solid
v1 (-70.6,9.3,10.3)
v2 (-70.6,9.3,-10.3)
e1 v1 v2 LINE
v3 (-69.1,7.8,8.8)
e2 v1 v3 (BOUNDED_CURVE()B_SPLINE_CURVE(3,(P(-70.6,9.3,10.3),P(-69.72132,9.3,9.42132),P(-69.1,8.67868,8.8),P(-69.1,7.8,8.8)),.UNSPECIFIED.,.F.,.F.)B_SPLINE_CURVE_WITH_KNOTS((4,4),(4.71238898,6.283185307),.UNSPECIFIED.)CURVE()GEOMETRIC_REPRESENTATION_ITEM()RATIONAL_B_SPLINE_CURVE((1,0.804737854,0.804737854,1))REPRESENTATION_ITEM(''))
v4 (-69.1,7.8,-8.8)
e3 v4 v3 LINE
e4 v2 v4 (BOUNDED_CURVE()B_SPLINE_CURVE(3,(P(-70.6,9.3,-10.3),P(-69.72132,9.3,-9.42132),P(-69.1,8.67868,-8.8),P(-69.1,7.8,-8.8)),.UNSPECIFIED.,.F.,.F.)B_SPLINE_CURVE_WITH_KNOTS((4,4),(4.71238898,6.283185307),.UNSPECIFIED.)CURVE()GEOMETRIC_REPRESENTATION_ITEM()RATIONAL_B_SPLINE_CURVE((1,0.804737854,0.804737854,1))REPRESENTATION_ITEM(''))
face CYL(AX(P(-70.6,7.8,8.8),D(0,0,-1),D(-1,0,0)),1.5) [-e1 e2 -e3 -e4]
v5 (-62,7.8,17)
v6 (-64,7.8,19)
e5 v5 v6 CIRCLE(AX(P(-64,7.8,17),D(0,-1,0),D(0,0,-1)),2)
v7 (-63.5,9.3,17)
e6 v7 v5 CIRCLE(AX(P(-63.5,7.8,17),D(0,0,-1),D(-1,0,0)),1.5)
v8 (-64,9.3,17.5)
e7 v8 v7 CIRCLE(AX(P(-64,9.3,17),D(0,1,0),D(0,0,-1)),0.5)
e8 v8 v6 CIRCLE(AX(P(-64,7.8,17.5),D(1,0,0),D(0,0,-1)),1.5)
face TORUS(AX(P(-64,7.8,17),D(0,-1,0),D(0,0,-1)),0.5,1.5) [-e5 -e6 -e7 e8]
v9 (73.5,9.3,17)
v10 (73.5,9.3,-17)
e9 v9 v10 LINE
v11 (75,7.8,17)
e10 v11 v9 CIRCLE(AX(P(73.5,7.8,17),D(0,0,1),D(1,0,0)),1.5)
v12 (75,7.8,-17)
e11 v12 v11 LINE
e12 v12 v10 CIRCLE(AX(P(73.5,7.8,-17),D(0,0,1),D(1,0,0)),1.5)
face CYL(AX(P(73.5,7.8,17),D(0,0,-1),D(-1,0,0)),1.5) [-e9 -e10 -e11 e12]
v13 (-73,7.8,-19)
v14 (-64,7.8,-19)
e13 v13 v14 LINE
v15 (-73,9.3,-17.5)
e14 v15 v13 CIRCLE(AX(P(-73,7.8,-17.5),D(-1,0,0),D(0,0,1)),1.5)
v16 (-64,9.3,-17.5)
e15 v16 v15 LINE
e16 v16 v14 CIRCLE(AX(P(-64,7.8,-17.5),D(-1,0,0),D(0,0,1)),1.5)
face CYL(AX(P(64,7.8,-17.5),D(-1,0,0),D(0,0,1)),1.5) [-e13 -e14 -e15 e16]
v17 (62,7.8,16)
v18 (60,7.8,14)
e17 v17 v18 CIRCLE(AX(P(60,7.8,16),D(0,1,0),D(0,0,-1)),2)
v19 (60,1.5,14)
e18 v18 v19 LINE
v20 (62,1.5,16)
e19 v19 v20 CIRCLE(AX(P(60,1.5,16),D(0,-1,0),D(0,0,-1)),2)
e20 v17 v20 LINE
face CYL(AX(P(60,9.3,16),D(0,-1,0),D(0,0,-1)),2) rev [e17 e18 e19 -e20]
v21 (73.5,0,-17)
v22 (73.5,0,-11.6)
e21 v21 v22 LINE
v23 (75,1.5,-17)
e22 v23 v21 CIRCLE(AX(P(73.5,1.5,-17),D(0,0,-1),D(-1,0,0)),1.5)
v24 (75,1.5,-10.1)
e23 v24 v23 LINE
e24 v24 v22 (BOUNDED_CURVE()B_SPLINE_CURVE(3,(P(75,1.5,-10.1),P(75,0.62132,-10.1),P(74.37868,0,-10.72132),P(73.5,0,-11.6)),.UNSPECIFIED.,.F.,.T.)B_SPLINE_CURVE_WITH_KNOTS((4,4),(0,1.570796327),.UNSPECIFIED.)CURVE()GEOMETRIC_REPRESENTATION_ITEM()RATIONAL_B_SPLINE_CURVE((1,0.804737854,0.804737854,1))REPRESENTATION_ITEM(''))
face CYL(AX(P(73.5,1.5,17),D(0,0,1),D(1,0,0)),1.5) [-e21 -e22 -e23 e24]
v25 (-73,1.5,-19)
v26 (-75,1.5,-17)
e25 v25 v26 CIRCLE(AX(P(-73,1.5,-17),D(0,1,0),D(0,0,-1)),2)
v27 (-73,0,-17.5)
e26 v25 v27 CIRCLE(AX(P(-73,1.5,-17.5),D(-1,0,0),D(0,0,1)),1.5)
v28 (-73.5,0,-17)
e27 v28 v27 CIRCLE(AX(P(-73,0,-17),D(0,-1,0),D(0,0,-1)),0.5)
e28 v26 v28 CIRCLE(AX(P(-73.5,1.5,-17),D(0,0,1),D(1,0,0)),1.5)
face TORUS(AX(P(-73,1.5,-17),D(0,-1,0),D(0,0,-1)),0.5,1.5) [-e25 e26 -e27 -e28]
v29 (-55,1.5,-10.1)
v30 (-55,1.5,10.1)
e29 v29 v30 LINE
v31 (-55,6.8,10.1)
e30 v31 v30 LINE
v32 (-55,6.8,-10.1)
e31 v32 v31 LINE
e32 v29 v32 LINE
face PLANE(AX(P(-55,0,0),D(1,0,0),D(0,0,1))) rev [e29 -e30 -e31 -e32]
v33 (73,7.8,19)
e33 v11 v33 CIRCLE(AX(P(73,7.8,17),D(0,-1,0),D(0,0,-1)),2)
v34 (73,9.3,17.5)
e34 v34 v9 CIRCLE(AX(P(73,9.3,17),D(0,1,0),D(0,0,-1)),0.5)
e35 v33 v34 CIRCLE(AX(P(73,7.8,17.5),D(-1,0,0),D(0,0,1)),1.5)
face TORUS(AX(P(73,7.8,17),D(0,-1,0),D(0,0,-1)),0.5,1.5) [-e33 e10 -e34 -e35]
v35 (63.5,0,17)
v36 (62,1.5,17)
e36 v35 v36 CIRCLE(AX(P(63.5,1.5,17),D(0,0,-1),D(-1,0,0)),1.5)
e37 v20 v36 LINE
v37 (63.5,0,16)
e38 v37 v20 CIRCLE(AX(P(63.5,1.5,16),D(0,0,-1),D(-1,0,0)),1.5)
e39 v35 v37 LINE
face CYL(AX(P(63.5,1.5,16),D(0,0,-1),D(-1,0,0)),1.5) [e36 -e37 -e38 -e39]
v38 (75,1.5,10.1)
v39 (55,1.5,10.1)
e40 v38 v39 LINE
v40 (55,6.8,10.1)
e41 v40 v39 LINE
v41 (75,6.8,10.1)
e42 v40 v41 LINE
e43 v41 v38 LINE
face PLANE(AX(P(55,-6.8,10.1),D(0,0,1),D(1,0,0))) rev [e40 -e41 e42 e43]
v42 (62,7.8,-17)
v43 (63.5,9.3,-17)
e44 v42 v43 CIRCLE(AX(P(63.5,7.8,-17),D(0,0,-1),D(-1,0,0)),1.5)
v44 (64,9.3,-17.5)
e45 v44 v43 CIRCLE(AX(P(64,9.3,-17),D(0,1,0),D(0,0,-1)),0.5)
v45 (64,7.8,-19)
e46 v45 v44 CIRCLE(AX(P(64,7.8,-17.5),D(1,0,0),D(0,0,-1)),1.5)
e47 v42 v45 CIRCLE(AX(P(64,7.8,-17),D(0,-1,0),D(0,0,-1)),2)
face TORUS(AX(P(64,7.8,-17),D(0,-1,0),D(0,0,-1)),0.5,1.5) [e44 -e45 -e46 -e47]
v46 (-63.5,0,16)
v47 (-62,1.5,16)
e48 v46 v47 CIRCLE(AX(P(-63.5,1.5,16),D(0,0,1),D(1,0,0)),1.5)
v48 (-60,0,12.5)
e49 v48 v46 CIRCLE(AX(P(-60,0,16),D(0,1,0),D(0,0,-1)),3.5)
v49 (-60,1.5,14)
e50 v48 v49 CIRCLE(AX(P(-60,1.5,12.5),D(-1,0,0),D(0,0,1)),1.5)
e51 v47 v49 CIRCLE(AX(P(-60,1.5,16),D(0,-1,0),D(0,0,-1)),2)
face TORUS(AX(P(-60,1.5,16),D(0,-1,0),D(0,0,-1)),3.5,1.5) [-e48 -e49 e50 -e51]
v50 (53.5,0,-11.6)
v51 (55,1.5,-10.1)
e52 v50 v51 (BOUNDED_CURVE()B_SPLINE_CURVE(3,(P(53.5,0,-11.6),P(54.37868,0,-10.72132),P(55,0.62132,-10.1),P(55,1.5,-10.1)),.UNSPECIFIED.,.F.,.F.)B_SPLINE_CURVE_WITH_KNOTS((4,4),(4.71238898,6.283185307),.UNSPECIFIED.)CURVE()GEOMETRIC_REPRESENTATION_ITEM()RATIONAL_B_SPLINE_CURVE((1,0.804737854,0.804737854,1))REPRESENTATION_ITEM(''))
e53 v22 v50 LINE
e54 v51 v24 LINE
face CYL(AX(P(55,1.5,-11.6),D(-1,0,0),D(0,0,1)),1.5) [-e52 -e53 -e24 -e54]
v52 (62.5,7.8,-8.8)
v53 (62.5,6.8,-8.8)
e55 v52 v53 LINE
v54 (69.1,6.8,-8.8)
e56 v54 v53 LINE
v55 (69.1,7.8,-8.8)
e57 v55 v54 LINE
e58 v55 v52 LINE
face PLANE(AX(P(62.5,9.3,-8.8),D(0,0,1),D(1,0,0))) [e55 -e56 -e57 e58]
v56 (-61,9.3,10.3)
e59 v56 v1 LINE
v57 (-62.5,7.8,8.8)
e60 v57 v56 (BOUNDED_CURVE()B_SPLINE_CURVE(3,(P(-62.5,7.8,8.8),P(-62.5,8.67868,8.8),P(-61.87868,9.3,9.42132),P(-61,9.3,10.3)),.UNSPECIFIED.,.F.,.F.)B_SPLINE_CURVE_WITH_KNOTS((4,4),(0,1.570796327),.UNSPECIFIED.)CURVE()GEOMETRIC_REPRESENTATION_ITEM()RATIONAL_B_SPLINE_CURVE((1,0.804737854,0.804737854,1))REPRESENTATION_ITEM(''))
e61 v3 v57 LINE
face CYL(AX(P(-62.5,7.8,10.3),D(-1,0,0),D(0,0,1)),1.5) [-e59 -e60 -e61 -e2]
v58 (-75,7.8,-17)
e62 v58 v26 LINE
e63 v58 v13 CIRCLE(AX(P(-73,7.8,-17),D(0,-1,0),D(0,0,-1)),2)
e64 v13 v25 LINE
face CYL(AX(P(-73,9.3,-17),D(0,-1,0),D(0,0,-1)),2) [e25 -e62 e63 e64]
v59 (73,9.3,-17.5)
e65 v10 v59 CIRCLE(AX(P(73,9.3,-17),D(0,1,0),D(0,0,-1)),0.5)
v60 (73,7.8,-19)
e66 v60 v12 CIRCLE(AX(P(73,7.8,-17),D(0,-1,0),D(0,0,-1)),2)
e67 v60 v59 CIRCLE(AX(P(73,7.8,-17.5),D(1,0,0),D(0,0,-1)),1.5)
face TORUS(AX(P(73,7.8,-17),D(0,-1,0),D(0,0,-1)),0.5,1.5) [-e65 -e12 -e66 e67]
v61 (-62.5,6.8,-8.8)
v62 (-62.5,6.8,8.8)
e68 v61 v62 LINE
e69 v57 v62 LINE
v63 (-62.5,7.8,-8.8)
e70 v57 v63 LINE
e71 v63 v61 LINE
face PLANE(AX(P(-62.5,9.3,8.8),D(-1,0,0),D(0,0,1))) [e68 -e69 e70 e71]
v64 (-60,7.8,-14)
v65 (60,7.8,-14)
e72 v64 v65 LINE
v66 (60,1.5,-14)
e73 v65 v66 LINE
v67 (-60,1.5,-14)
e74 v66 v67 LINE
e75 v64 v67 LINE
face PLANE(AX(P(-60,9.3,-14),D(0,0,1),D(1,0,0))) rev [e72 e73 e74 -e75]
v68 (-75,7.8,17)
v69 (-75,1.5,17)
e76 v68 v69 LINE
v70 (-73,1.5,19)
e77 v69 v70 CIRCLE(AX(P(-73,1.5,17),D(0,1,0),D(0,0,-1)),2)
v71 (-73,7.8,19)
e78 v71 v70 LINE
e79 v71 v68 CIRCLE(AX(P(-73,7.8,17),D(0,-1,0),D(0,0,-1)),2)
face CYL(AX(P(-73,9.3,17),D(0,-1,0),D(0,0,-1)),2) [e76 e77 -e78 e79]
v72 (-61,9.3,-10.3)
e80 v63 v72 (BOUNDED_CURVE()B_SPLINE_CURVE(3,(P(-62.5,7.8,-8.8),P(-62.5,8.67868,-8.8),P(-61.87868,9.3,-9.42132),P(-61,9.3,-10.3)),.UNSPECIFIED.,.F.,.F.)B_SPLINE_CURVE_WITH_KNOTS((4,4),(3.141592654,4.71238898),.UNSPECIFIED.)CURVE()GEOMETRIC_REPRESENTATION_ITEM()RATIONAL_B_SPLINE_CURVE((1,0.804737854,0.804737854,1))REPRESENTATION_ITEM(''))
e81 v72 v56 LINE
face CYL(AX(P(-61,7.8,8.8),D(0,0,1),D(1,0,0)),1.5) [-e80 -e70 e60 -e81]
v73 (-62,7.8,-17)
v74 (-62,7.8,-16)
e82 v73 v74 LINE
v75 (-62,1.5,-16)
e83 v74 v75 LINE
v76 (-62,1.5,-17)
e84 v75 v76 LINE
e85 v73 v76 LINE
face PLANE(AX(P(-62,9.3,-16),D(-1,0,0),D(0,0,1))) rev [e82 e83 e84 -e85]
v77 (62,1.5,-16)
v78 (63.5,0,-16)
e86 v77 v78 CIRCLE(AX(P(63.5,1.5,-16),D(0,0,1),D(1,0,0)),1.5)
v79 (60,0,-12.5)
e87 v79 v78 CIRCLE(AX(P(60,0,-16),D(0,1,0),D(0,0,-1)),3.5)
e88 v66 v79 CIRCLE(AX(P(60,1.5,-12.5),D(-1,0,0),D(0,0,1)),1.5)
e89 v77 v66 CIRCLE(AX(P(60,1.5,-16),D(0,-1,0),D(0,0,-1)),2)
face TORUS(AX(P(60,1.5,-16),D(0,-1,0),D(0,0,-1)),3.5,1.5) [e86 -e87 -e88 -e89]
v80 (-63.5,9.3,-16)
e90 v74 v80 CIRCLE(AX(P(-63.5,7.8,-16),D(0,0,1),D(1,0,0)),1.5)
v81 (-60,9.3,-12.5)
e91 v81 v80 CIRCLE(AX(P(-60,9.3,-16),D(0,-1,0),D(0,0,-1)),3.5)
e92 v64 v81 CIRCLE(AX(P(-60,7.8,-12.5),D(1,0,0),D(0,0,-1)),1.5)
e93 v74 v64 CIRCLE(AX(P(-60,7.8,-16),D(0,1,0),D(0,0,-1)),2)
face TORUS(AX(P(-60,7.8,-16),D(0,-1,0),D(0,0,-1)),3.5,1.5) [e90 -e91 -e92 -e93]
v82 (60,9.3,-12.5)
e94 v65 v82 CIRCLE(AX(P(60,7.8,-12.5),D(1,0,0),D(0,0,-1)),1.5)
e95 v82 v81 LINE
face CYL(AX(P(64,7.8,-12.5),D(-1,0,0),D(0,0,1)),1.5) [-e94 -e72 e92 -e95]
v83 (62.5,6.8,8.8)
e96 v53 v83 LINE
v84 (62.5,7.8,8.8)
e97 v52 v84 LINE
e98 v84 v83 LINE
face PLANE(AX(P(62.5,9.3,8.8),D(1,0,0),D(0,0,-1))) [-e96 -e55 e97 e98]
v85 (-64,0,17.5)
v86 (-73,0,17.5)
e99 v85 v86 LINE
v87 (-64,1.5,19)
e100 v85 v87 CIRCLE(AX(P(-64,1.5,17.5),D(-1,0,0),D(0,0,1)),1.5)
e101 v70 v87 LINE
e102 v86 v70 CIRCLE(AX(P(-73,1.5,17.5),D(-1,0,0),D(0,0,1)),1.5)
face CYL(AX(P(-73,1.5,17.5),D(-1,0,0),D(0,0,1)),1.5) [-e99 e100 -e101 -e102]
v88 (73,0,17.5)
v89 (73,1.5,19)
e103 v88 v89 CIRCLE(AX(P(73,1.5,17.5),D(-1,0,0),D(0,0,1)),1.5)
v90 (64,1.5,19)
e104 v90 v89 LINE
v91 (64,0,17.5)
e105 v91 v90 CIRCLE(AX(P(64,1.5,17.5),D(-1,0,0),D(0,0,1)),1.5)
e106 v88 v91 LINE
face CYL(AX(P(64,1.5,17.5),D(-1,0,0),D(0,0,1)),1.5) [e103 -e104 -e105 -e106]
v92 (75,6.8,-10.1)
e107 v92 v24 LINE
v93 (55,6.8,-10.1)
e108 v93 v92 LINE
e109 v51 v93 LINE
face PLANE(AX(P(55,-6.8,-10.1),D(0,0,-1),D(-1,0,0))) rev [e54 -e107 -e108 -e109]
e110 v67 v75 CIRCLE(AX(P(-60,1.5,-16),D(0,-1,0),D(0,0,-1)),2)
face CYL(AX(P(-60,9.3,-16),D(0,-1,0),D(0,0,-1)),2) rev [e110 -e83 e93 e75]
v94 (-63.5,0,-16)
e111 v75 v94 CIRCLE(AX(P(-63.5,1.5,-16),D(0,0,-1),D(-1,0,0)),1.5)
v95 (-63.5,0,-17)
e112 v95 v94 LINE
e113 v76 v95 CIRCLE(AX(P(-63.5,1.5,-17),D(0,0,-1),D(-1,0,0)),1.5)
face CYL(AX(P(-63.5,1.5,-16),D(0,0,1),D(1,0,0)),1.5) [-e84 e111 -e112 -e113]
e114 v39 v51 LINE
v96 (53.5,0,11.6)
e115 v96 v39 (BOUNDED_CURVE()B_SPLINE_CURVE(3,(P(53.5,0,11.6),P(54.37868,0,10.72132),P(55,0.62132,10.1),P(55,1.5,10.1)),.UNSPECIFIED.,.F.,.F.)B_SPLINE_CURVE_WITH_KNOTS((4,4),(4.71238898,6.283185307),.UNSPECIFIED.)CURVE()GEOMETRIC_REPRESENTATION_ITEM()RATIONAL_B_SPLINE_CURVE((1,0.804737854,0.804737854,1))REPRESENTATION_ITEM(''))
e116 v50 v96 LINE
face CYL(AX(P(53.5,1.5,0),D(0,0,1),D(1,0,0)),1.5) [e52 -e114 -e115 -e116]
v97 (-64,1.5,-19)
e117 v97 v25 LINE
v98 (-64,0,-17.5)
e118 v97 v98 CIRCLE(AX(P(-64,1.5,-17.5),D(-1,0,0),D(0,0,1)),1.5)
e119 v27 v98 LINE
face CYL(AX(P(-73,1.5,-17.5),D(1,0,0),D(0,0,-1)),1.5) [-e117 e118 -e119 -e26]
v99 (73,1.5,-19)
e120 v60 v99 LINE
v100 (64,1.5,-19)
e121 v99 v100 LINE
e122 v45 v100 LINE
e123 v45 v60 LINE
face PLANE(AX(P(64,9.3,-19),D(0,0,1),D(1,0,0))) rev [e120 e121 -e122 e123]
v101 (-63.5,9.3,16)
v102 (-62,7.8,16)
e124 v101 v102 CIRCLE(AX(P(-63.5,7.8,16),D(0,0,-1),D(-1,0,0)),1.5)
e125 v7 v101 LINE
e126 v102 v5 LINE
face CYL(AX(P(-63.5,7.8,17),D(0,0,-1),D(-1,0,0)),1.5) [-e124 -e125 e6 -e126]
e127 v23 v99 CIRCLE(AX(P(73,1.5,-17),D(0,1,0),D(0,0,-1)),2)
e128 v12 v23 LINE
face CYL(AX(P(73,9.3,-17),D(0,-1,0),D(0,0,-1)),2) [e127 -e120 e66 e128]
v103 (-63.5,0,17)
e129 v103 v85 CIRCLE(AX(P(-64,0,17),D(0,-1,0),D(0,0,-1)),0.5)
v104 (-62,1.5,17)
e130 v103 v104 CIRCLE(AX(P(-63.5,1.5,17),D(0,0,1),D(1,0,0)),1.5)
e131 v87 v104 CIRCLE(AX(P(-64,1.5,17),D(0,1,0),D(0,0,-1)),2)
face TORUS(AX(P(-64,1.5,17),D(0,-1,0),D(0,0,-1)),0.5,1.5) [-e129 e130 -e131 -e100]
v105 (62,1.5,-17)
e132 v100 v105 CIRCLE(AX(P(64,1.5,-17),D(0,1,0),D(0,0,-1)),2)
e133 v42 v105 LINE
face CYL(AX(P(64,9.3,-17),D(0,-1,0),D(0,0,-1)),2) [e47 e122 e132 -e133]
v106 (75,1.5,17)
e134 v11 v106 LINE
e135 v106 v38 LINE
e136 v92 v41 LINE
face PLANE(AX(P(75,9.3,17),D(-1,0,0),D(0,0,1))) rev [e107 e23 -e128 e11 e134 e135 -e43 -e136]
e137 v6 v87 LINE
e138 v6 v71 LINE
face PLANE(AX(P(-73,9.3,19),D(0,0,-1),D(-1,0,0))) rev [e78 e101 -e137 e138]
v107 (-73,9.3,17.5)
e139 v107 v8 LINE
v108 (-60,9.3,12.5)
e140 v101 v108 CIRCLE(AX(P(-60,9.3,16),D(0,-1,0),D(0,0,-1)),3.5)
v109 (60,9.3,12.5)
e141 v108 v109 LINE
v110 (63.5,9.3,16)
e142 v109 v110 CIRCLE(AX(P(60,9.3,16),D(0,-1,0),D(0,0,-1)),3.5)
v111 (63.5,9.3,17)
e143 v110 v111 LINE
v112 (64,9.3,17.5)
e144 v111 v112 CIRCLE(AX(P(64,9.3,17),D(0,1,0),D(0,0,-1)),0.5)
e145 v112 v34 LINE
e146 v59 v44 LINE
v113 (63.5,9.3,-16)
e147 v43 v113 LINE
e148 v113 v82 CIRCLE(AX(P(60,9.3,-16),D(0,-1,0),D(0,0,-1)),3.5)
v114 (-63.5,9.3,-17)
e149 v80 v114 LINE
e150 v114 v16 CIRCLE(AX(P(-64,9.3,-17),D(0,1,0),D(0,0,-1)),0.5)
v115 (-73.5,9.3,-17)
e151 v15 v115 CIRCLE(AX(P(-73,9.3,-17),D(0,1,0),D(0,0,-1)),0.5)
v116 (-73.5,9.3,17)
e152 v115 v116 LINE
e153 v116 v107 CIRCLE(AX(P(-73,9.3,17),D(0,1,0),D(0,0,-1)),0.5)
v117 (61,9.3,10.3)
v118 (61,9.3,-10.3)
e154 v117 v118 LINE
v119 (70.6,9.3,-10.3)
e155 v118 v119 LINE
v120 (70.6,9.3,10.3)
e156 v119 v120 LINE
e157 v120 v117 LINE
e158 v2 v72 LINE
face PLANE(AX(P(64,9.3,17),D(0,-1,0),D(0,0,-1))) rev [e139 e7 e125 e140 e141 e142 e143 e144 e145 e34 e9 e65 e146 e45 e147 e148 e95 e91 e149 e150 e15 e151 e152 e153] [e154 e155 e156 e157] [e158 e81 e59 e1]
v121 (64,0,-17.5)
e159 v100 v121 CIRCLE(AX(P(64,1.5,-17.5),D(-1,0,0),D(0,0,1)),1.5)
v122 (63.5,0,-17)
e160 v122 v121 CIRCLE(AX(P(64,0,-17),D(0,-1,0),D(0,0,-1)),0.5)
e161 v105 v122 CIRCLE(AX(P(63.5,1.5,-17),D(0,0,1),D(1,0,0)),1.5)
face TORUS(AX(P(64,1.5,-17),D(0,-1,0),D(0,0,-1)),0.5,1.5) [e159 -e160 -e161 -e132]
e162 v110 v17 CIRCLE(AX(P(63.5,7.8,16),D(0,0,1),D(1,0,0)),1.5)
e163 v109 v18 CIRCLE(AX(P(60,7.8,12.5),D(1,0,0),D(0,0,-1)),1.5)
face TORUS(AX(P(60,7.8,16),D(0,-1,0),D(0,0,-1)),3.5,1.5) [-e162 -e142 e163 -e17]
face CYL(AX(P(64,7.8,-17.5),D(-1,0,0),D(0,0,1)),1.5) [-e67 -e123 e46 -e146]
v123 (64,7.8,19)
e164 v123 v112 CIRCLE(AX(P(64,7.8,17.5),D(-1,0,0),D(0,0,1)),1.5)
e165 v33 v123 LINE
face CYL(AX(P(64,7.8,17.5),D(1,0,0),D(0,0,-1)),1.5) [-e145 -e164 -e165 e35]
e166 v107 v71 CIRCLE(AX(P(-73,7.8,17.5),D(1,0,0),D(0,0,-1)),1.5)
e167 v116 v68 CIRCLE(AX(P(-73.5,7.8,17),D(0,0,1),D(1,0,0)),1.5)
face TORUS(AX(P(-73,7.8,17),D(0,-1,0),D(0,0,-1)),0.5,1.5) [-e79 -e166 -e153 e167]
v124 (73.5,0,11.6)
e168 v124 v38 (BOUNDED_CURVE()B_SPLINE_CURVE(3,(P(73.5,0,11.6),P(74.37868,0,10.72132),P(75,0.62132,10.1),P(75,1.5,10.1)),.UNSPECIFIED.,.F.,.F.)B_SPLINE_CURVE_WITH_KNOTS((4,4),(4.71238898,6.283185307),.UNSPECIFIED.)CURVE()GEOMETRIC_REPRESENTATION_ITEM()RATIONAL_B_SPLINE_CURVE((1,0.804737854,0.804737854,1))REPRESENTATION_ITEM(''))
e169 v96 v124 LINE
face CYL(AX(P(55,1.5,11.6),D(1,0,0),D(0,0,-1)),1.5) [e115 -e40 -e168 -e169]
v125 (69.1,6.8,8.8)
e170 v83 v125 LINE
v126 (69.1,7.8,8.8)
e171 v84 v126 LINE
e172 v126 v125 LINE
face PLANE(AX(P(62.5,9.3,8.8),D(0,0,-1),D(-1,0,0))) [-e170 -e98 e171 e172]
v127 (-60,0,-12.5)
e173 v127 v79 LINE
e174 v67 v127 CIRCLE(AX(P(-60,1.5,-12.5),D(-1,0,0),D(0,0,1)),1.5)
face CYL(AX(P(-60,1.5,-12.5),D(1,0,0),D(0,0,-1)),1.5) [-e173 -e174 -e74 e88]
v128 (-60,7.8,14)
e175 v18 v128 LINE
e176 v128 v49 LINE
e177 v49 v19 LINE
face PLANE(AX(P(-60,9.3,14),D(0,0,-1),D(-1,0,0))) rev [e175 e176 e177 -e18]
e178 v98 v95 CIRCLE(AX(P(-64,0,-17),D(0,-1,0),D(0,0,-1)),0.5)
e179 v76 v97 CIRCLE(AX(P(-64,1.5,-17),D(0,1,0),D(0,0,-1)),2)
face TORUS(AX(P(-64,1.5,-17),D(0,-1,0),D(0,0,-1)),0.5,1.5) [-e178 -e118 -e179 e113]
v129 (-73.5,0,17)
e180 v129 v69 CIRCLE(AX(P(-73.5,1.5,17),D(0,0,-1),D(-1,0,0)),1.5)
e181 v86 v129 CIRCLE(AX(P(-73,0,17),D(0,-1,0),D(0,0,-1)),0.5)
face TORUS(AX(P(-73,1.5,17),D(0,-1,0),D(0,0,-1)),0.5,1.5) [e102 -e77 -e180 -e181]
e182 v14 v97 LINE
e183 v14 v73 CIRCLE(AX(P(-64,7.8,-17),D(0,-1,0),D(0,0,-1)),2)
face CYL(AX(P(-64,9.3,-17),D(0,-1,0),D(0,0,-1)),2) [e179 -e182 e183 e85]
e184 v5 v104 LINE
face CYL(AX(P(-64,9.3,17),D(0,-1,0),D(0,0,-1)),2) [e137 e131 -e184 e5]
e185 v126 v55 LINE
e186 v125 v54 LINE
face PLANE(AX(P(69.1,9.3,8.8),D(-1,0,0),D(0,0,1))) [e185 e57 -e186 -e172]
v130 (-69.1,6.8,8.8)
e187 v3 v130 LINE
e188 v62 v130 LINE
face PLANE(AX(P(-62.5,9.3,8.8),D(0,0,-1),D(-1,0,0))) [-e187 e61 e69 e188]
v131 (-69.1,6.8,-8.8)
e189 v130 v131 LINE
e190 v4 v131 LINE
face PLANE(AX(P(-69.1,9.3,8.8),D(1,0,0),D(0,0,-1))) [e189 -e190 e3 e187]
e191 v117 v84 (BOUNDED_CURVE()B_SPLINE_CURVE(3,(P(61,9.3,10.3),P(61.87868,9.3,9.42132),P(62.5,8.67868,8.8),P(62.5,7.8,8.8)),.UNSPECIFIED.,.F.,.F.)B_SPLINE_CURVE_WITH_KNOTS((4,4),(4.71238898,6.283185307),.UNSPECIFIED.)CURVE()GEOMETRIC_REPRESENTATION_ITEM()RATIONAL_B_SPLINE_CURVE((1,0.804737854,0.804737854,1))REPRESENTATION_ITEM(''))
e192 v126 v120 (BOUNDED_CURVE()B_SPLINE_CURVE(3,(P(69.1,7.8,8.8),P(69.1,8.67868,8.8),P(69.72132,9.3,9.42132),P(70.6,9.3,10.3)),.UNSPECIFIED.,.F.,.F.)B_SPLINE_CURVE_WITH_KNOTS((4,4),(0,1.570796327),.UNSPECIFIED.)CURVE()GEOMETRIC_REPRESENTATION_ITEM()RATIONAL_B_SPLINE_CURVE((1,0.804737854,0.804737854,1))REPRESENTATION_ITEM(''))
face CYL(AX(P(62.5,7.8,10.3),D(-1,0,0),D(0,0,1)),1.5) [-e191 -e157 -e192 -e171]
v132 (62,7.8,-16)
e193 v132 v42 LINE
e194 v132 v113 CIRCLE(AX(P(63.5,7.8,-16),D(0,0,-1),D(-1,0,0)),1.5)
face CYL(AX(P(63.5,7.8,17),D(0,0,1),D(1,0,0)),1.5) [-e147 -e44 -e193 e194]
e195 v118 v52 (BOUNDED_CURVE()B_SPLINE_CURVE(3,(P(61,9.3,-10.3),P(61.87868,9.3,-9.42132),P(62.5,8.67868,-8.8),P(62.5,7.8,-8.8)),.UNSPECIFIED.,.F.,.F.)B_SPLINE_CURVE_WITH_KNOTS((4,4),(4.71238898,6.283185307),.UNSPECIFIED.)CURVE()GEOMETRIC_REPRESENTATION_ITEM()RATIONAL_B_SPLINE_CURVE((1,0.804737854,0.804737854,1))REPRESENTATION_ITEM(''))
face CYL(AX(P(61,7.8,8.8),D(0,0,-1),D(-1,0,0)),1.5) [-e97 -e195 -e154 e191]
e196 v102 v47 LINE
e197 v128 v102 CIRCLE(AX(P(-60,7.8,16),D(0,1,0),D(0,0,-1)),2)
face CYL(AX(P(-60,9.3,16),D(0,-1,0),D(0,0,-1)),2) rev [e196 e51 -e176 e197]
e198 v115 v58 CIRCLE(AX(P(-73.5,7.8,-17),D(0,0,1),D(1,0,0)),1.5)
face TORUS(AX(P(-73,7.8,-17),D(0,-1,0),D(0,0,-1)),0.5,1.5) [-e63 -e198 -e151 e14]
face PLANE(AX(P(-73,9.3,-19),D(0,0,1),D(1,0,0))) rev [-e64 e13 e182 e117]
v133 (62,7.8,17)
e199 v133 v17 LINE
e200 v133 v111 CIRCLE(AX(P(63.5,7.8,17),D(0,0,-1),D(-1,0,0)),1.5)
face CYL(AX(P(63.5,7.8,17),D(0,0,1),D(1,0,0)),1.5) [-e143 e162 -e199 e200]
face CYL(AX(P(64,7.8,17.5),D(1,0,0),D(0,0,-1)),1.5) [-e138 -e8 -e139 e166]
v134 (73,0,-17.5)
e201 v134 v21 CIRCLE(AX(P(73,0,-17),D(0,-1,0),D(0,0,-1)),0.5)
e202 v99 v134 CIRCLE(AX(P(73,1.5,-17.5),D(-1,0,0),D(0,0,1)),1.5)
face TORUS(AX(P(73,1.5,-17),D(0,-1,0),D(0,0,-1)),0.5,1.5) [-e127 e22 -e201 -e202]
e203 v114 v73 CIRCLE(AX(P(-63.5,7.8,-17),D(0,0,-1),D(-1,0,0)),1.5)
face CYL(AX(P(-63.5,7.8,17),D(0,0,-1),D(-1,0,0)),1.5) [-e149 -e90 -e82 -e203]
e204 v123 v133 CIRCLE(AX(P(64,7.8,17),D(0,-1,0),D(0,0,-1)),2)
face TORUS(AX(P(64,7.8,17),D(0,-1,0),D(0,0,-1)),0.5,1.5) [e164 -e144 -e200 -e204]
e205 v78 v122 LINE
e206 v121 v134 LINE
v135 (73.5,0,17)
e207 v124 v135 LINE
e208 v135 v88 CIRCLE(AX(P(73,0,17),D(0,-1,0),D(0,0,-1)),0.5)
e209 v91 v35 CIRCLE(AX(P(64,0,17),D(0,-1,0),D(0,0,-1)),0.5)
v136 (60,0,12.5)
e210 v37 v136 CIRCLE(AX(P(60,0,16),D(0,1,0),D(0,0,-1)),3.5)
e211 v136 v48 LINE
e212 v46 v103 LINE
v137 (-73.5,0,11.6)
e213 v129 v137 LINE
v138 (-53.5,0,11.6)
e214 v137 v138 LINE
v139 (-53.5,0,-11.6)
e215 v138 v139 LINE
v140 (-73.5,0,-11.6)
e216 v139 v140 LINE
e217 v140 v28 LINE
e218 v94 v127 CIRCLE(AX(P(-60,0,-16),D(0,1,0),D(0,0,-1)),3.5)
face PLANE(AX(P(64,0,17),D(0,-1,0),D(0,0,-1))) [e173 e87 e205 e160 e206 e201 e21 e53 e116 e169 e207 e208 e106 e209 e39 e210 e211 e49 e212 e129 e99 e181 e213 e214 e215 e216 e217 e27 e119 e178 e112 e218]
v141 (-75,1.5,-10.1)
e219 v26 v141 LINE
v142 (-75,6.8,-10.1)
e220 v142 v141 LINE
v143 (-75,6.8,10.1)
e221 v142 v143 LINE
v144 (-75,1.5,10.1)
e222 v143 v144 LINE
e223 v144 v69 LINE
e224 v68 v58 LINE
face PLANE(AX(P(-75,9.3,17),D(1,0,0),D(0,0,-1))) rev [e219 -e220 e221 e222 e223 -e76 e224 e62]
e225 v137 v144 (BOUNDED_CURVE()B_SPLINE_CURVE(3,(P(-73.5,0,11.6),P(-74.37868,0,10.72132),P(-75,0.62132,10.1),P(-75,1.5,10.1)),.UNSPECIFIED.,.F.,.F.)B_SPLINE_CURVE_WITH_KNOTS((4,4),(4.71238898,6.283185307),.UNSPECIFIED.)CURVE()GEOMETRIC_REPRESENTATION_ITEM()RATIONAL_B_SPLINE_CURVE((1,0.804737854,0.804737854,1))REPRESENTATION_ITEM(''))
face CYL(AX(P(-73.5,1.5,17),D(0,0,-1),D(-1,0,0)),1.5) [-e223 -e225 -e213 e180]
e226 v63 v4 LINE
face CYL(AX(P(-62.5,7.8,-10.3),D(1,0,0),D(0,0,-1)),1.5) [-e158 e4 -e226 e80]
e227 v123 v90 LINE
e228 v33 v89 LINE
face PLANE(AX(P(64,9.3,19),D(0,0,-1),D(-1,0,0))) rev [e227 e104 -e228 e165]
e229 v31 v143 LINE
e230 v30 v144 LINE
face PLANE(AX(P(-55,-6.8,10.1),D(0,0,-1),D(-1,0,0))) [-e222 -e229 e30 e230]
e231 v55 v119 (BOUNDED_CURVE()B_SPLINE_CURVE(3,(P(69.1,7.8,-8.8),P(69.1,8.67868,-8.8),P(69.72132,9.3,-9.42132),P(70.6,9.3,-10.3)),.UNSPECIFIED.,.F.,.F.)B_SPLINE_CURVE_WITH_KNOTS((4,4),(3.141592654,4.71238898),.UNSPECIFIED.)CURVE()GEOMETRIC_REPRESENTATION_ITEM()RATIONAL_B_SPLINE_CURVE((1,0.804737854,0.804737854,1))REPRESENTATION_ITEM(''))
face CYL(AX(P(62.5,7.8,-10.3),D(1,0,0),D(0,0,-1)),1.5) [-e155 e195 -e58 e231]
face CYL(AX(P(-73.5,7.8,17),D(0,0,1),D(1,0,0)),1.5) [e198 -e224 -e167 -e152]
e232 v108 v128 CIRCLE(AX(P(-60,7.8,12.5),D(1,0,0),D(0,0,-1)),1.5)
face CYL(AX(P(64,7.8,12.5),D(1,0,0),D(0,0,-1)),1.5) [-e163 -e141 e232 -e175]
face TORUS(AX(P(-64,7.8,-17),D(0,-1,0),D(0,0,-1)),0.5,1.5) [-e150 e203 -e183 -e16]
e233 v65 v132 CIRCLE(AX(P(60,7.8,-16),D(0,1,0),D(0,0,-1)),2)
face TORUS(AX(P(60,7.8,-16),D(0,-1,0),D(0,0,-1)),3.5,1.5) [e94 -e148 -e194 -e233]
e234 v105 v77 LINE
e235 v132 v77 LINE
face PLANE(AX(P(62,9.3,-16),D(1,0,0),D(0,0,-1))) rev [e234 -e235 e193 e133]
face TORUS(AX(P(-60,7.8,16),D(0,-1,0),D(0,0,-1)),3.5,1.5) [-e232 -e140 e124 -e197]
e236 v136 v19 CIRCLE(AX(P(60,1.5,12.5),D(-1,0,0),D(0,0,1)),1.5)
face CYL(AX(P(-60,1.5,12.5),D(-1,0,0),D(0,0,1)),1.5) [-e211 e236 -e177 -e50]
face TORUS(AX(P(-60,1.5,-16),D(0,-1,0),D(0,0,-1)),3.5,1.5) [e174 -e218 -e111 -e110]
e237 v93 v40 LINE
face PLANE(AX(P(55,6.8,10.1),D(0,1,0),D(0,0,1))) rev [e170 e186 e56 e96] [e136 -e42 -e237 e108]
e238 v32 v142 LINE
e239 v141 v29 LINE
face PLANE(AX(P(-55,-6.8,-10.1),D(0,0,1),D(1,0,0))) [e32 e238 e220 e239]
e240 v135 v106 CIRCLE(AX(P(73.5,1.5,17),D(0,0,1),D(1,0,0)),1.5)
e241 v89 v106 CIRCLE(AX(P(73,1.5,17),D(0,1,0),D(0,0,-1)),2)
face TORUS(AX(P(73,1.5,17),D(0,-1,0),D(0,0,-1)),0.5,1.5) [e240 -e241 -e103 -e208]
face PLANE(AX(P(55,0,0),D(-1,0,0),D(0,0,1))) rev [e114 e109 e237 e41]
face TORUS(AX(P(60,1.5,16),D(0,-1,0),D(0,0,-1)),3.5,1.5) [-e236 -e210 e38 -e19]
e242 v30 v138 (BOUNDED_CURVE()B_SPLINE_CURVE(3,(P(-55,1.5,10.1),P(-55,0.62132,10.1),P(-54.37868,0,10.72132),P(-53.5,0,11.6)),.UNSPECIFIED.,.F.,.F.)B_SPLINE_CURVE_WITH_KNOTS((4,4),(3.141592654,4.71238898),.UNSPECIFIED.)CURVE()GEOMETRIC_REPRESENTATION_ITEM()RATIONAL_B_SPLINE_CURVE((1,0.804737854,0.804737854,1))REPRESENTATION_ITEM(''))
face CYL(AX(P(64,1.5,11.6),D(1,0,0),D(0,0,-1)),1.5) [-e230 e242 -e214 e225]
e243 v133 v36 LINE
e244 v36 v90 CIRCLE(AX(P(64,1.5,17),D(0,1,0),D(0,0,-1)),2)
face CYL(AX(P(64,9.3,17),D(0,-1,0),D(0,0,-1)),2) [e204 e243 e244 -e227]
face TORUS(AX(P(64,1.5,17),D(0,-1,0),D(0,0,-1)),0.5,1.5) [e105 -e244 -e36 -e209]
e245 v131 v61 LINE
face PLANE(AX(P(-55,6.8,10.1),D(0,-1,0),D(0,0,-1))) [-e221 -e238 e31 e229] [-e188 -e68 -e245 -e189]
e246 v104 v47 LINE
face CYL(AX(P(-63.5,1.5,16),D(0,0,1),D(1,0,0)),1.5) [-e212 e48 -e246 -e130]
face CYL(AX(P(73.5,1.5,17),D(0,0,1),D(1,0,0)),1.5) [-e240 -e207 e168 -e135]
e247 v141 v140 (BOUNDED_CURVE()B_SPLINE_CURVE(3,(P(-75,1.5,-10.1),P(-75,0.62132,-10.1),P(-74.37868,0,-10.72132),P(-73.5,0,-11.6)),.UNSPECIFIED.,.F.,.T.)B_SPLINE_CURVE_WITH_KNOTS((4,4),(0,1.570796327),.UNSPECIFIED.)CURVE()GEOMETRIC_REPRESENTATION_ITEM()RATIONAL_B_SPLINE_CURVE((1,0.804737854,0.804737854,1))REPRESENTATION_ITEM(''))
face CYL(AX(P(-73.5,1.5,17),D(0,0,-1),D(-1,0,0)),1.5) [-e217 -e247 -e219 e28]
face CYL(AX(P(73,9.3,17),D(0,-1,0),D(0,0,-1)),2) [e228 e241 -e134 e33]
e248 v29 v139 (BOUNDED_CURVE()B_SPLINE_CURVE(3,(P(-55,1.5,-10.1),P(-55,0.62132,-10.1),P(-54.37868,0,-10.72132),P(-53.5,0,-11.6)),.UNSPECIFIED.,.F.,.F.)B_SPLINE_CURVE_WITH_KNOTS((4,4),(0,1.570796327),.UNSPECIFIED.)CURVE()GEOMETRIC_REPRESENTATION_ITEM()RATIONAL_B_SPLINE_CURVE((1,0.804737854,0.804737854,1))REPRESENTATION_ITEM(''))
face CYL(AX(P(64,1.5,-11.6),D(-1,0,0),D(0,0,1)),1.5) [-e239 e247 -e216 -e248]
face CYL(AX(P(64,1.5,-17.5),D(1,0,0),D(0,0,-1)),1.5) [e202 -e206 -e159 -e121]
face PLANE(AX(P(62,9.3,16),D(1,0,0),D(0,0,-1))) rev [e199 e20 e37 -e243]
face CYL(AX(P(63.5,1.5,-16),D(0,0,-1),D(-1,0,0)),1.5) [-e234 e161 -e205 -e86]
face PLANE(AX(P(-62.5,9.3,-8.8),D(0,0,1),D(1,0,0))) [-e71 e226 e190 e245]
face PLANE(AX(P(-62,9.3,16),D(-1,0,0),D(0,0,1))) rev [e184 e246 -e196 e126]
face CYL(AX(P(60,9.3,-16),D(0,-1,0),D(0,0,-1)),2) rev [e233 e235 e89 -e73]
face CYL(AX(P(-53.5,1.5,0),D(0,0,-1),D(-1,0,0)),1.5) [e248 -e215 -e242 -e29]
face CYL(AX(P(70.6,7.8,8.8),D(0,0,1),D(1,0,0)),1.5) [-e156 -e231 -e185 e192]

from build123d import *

# Parameters (mm, degrees)
SKETCH_1_W          = 6.6
SKETCH_1_H          = 17.6
EXTRUDE_1_DEPTH     = 9.3
SKETCH_2_W          = 20.2
SKETCH_2_H          = 13.6
CUT_EXTRUDE_1_DEPTH = 20
FILLET_2_R          = 1.5


with BuildPart() as part:
    # 草图1 → 凸台-拉伸1 (new body)
    with BuildSketch(Plane(origin=(0, 0, 0), x_dir=(1, 0, 0), z_dir=(0, 1, 0))):
        with BuildLine():
            Line((-62, 16), (-62, 17))
            ThreePointArc((-62, 17), (-62.585786438, 18.414213562), (-64, 19))
            Line((-64, 19), (-73, 19))
            ThreePointArc((-73, 19), (-74.414213562, 18.414213562), (-75, 17))
            Line((-75, 17), (-75, -17))
            ThreePointArc((-75, -17), (-74.414213562, -18.414213562), (-73, -19))
            Line((-73, -19), (-64, -19))
            ThreePointArc((-64, -19), (-62.585786438, -18.414213562), (-62, -17))
            Line((-62, -17), (-62, -16))
            ThreePointArc((-62, -16), (-61.414213562, -14.585786438), (-60, -14))
            Line((-60, -14), (60, -14))
            ThreePointArc((60, -14), (61.414213562, -14.585786438), (62, -16))
            Line((62, -16), (62, -17))
            ThreePointArc((62, -17), (62.585786438, -18.414213562), (64, -19))
            Line((64, -19), (73, -19))
            ThreePointArc((73, -19), (74.414213562, -18.414213562), (75, -17))
            Line((75, -17), (75, 17))
            ThreePointArc((75, 17), (74.414213562, 18.414213562), (73, 19))
            Line((73, 19), (64, 19))
            ThreePointArc((64, 19), (62.585786438, 18.414213562), (62, 17))
            Line((62, 17), (62, 16))
            ThreePointArc((62, 16), (61.414213562, 14.585786438), (60, 14))
            Line((60, 14), (-60, 14))
            ThreePointArc((-60, 14), (-61.414213562, 14.585786438), (-62, 16))
        make_face()
        with Locations((65.8, 0)):
            Rectangle(SKETCH_1_W, SKETCH_1_H, mode=Mode.SUBTRACT)
        with Locations((-65.8, 0)):
            Rectangle(SKETCH_1_W, SKETCH_1_H, mode=Mode.SUBTRACT)
    extrude(amount=EXTRUDE_1_DEPTH)

    # 草图2 → 切除-拉伸1 (cut)
    with BuildSketch(Plane(origin=(75, 0, 0), x_dir=(0, 0, -1), z_dir=(1, 0, 0))):
        Rectangle(SKETCH_2_W, SKETCH_2_H)
    cut_extrude_1 = extrude(amount=-CUT_EXTRUDE_1_DEPTH, mode=Mode.SUBTRACT)

    # 镜向1: 切除-拉伸1 across plane
    add(cut_extrude_1.mirror(Plane(origin=(0, 0, 0), x_dir=(0, 0, 1), z_dir=(1, 0, 0))), mode=Mode.SUBTRACT)

    # 圆角2
    fillet_2_edges = [part.edges().sort_by_distance(p)[0] for p in [
        (74.414213562, 9.3, 18.414213562),
        (55, 0, 0),
        (65, 0, -10.1),
        (65, 0, 10.1),
        (-75, 0, 13.55),
        (-55, 0, 0),
        (-65, 0, -10.1),
        (75, 9.3, 0),
        (-65, 0, 10.1),
        (74.414213562, 9.3, -18.414213562),
        (68.5, 9.3, -19),
        (62, 0, 16.5),
        (61.414213562, 0, 14.585786438),
        (0, 0, 14),
        (-61.414213562, 0, 14.585786438),
        (62.585786438, 9.3, -18.414213562),
        (-62, 0, 16.5),
        (-62.585786438, 0, 18.414213562),
        (-68.5, 0, 19),
        (-74.414213562, 0, 18.414213562),
        (-75, 0, -13.55),
        (-74.414213562, 0, -18.414213562),
        (-68.5, 0, -19),
        (-62.585786438, 0, -18.414213562),
        (62, 9.3, -16.5),
        (-62, 0, -16.5),
        (-61.414213562, 0, -14.585786438),
        (0, 0, -14),
        (61.414213562, 0, -14.585786438),
        (62, 0, -16.5),
        (62.585786438, 0, -18.414213562),
        (68.5, 0, -19),
        (61.414213562, 9.3, -14.585786438),
        (74.414213562, 0, -18.414213562),
        (75, 0, 13.55),
        (74.414213562, 0, 18.414213562),
        (68.5, 0, 19),
        (62.585786438, 0, 18.414213562),
        (0, 9.3, -14),
        (-61.414213562, 9.3, -14.585786438),
        (-62, 9.3, -16.5),
        (62.585786438, 9.3, 18.414213562),
        (-62.585786438, 9.3, -18.414213562),
        (-68.5, 9.3, -19),
        (-74.414213562, 9.3, -18.414213562),
        (-75, 9.3, 0),
        (-74.414213562, 9.3, 18.414213562),
        (-68.5, 9.3, 19),
        (-62.585786438, 9.3, 18.414213562),
        (69.1, 9.3, 0),
        (65.8, 9.3, -8.8),
        (-62, 9.3, 16.5),
        (62.5, 9.3, 0),
        (65.8, 9.3, 8.8),
        (-61.414213562, 9.3, 14.585786438),
        (0, 9.3, 14),
        (68.5, 9.3, 19),
        (61.414213562, 9.3, 14.585786438),
        (62, 9.3, 16.5),
        (-62.5, 9.3, 0),
        (-65.8, 9.3, -8.8),
        (-69.1, 9.3, 0),
        (-65.8, 9.3, 8.8),
        (75, 0, -13.55),
    ]]
    fillet(fillet_2_edges, radius=FILLET_2_R)


solid = part.part
